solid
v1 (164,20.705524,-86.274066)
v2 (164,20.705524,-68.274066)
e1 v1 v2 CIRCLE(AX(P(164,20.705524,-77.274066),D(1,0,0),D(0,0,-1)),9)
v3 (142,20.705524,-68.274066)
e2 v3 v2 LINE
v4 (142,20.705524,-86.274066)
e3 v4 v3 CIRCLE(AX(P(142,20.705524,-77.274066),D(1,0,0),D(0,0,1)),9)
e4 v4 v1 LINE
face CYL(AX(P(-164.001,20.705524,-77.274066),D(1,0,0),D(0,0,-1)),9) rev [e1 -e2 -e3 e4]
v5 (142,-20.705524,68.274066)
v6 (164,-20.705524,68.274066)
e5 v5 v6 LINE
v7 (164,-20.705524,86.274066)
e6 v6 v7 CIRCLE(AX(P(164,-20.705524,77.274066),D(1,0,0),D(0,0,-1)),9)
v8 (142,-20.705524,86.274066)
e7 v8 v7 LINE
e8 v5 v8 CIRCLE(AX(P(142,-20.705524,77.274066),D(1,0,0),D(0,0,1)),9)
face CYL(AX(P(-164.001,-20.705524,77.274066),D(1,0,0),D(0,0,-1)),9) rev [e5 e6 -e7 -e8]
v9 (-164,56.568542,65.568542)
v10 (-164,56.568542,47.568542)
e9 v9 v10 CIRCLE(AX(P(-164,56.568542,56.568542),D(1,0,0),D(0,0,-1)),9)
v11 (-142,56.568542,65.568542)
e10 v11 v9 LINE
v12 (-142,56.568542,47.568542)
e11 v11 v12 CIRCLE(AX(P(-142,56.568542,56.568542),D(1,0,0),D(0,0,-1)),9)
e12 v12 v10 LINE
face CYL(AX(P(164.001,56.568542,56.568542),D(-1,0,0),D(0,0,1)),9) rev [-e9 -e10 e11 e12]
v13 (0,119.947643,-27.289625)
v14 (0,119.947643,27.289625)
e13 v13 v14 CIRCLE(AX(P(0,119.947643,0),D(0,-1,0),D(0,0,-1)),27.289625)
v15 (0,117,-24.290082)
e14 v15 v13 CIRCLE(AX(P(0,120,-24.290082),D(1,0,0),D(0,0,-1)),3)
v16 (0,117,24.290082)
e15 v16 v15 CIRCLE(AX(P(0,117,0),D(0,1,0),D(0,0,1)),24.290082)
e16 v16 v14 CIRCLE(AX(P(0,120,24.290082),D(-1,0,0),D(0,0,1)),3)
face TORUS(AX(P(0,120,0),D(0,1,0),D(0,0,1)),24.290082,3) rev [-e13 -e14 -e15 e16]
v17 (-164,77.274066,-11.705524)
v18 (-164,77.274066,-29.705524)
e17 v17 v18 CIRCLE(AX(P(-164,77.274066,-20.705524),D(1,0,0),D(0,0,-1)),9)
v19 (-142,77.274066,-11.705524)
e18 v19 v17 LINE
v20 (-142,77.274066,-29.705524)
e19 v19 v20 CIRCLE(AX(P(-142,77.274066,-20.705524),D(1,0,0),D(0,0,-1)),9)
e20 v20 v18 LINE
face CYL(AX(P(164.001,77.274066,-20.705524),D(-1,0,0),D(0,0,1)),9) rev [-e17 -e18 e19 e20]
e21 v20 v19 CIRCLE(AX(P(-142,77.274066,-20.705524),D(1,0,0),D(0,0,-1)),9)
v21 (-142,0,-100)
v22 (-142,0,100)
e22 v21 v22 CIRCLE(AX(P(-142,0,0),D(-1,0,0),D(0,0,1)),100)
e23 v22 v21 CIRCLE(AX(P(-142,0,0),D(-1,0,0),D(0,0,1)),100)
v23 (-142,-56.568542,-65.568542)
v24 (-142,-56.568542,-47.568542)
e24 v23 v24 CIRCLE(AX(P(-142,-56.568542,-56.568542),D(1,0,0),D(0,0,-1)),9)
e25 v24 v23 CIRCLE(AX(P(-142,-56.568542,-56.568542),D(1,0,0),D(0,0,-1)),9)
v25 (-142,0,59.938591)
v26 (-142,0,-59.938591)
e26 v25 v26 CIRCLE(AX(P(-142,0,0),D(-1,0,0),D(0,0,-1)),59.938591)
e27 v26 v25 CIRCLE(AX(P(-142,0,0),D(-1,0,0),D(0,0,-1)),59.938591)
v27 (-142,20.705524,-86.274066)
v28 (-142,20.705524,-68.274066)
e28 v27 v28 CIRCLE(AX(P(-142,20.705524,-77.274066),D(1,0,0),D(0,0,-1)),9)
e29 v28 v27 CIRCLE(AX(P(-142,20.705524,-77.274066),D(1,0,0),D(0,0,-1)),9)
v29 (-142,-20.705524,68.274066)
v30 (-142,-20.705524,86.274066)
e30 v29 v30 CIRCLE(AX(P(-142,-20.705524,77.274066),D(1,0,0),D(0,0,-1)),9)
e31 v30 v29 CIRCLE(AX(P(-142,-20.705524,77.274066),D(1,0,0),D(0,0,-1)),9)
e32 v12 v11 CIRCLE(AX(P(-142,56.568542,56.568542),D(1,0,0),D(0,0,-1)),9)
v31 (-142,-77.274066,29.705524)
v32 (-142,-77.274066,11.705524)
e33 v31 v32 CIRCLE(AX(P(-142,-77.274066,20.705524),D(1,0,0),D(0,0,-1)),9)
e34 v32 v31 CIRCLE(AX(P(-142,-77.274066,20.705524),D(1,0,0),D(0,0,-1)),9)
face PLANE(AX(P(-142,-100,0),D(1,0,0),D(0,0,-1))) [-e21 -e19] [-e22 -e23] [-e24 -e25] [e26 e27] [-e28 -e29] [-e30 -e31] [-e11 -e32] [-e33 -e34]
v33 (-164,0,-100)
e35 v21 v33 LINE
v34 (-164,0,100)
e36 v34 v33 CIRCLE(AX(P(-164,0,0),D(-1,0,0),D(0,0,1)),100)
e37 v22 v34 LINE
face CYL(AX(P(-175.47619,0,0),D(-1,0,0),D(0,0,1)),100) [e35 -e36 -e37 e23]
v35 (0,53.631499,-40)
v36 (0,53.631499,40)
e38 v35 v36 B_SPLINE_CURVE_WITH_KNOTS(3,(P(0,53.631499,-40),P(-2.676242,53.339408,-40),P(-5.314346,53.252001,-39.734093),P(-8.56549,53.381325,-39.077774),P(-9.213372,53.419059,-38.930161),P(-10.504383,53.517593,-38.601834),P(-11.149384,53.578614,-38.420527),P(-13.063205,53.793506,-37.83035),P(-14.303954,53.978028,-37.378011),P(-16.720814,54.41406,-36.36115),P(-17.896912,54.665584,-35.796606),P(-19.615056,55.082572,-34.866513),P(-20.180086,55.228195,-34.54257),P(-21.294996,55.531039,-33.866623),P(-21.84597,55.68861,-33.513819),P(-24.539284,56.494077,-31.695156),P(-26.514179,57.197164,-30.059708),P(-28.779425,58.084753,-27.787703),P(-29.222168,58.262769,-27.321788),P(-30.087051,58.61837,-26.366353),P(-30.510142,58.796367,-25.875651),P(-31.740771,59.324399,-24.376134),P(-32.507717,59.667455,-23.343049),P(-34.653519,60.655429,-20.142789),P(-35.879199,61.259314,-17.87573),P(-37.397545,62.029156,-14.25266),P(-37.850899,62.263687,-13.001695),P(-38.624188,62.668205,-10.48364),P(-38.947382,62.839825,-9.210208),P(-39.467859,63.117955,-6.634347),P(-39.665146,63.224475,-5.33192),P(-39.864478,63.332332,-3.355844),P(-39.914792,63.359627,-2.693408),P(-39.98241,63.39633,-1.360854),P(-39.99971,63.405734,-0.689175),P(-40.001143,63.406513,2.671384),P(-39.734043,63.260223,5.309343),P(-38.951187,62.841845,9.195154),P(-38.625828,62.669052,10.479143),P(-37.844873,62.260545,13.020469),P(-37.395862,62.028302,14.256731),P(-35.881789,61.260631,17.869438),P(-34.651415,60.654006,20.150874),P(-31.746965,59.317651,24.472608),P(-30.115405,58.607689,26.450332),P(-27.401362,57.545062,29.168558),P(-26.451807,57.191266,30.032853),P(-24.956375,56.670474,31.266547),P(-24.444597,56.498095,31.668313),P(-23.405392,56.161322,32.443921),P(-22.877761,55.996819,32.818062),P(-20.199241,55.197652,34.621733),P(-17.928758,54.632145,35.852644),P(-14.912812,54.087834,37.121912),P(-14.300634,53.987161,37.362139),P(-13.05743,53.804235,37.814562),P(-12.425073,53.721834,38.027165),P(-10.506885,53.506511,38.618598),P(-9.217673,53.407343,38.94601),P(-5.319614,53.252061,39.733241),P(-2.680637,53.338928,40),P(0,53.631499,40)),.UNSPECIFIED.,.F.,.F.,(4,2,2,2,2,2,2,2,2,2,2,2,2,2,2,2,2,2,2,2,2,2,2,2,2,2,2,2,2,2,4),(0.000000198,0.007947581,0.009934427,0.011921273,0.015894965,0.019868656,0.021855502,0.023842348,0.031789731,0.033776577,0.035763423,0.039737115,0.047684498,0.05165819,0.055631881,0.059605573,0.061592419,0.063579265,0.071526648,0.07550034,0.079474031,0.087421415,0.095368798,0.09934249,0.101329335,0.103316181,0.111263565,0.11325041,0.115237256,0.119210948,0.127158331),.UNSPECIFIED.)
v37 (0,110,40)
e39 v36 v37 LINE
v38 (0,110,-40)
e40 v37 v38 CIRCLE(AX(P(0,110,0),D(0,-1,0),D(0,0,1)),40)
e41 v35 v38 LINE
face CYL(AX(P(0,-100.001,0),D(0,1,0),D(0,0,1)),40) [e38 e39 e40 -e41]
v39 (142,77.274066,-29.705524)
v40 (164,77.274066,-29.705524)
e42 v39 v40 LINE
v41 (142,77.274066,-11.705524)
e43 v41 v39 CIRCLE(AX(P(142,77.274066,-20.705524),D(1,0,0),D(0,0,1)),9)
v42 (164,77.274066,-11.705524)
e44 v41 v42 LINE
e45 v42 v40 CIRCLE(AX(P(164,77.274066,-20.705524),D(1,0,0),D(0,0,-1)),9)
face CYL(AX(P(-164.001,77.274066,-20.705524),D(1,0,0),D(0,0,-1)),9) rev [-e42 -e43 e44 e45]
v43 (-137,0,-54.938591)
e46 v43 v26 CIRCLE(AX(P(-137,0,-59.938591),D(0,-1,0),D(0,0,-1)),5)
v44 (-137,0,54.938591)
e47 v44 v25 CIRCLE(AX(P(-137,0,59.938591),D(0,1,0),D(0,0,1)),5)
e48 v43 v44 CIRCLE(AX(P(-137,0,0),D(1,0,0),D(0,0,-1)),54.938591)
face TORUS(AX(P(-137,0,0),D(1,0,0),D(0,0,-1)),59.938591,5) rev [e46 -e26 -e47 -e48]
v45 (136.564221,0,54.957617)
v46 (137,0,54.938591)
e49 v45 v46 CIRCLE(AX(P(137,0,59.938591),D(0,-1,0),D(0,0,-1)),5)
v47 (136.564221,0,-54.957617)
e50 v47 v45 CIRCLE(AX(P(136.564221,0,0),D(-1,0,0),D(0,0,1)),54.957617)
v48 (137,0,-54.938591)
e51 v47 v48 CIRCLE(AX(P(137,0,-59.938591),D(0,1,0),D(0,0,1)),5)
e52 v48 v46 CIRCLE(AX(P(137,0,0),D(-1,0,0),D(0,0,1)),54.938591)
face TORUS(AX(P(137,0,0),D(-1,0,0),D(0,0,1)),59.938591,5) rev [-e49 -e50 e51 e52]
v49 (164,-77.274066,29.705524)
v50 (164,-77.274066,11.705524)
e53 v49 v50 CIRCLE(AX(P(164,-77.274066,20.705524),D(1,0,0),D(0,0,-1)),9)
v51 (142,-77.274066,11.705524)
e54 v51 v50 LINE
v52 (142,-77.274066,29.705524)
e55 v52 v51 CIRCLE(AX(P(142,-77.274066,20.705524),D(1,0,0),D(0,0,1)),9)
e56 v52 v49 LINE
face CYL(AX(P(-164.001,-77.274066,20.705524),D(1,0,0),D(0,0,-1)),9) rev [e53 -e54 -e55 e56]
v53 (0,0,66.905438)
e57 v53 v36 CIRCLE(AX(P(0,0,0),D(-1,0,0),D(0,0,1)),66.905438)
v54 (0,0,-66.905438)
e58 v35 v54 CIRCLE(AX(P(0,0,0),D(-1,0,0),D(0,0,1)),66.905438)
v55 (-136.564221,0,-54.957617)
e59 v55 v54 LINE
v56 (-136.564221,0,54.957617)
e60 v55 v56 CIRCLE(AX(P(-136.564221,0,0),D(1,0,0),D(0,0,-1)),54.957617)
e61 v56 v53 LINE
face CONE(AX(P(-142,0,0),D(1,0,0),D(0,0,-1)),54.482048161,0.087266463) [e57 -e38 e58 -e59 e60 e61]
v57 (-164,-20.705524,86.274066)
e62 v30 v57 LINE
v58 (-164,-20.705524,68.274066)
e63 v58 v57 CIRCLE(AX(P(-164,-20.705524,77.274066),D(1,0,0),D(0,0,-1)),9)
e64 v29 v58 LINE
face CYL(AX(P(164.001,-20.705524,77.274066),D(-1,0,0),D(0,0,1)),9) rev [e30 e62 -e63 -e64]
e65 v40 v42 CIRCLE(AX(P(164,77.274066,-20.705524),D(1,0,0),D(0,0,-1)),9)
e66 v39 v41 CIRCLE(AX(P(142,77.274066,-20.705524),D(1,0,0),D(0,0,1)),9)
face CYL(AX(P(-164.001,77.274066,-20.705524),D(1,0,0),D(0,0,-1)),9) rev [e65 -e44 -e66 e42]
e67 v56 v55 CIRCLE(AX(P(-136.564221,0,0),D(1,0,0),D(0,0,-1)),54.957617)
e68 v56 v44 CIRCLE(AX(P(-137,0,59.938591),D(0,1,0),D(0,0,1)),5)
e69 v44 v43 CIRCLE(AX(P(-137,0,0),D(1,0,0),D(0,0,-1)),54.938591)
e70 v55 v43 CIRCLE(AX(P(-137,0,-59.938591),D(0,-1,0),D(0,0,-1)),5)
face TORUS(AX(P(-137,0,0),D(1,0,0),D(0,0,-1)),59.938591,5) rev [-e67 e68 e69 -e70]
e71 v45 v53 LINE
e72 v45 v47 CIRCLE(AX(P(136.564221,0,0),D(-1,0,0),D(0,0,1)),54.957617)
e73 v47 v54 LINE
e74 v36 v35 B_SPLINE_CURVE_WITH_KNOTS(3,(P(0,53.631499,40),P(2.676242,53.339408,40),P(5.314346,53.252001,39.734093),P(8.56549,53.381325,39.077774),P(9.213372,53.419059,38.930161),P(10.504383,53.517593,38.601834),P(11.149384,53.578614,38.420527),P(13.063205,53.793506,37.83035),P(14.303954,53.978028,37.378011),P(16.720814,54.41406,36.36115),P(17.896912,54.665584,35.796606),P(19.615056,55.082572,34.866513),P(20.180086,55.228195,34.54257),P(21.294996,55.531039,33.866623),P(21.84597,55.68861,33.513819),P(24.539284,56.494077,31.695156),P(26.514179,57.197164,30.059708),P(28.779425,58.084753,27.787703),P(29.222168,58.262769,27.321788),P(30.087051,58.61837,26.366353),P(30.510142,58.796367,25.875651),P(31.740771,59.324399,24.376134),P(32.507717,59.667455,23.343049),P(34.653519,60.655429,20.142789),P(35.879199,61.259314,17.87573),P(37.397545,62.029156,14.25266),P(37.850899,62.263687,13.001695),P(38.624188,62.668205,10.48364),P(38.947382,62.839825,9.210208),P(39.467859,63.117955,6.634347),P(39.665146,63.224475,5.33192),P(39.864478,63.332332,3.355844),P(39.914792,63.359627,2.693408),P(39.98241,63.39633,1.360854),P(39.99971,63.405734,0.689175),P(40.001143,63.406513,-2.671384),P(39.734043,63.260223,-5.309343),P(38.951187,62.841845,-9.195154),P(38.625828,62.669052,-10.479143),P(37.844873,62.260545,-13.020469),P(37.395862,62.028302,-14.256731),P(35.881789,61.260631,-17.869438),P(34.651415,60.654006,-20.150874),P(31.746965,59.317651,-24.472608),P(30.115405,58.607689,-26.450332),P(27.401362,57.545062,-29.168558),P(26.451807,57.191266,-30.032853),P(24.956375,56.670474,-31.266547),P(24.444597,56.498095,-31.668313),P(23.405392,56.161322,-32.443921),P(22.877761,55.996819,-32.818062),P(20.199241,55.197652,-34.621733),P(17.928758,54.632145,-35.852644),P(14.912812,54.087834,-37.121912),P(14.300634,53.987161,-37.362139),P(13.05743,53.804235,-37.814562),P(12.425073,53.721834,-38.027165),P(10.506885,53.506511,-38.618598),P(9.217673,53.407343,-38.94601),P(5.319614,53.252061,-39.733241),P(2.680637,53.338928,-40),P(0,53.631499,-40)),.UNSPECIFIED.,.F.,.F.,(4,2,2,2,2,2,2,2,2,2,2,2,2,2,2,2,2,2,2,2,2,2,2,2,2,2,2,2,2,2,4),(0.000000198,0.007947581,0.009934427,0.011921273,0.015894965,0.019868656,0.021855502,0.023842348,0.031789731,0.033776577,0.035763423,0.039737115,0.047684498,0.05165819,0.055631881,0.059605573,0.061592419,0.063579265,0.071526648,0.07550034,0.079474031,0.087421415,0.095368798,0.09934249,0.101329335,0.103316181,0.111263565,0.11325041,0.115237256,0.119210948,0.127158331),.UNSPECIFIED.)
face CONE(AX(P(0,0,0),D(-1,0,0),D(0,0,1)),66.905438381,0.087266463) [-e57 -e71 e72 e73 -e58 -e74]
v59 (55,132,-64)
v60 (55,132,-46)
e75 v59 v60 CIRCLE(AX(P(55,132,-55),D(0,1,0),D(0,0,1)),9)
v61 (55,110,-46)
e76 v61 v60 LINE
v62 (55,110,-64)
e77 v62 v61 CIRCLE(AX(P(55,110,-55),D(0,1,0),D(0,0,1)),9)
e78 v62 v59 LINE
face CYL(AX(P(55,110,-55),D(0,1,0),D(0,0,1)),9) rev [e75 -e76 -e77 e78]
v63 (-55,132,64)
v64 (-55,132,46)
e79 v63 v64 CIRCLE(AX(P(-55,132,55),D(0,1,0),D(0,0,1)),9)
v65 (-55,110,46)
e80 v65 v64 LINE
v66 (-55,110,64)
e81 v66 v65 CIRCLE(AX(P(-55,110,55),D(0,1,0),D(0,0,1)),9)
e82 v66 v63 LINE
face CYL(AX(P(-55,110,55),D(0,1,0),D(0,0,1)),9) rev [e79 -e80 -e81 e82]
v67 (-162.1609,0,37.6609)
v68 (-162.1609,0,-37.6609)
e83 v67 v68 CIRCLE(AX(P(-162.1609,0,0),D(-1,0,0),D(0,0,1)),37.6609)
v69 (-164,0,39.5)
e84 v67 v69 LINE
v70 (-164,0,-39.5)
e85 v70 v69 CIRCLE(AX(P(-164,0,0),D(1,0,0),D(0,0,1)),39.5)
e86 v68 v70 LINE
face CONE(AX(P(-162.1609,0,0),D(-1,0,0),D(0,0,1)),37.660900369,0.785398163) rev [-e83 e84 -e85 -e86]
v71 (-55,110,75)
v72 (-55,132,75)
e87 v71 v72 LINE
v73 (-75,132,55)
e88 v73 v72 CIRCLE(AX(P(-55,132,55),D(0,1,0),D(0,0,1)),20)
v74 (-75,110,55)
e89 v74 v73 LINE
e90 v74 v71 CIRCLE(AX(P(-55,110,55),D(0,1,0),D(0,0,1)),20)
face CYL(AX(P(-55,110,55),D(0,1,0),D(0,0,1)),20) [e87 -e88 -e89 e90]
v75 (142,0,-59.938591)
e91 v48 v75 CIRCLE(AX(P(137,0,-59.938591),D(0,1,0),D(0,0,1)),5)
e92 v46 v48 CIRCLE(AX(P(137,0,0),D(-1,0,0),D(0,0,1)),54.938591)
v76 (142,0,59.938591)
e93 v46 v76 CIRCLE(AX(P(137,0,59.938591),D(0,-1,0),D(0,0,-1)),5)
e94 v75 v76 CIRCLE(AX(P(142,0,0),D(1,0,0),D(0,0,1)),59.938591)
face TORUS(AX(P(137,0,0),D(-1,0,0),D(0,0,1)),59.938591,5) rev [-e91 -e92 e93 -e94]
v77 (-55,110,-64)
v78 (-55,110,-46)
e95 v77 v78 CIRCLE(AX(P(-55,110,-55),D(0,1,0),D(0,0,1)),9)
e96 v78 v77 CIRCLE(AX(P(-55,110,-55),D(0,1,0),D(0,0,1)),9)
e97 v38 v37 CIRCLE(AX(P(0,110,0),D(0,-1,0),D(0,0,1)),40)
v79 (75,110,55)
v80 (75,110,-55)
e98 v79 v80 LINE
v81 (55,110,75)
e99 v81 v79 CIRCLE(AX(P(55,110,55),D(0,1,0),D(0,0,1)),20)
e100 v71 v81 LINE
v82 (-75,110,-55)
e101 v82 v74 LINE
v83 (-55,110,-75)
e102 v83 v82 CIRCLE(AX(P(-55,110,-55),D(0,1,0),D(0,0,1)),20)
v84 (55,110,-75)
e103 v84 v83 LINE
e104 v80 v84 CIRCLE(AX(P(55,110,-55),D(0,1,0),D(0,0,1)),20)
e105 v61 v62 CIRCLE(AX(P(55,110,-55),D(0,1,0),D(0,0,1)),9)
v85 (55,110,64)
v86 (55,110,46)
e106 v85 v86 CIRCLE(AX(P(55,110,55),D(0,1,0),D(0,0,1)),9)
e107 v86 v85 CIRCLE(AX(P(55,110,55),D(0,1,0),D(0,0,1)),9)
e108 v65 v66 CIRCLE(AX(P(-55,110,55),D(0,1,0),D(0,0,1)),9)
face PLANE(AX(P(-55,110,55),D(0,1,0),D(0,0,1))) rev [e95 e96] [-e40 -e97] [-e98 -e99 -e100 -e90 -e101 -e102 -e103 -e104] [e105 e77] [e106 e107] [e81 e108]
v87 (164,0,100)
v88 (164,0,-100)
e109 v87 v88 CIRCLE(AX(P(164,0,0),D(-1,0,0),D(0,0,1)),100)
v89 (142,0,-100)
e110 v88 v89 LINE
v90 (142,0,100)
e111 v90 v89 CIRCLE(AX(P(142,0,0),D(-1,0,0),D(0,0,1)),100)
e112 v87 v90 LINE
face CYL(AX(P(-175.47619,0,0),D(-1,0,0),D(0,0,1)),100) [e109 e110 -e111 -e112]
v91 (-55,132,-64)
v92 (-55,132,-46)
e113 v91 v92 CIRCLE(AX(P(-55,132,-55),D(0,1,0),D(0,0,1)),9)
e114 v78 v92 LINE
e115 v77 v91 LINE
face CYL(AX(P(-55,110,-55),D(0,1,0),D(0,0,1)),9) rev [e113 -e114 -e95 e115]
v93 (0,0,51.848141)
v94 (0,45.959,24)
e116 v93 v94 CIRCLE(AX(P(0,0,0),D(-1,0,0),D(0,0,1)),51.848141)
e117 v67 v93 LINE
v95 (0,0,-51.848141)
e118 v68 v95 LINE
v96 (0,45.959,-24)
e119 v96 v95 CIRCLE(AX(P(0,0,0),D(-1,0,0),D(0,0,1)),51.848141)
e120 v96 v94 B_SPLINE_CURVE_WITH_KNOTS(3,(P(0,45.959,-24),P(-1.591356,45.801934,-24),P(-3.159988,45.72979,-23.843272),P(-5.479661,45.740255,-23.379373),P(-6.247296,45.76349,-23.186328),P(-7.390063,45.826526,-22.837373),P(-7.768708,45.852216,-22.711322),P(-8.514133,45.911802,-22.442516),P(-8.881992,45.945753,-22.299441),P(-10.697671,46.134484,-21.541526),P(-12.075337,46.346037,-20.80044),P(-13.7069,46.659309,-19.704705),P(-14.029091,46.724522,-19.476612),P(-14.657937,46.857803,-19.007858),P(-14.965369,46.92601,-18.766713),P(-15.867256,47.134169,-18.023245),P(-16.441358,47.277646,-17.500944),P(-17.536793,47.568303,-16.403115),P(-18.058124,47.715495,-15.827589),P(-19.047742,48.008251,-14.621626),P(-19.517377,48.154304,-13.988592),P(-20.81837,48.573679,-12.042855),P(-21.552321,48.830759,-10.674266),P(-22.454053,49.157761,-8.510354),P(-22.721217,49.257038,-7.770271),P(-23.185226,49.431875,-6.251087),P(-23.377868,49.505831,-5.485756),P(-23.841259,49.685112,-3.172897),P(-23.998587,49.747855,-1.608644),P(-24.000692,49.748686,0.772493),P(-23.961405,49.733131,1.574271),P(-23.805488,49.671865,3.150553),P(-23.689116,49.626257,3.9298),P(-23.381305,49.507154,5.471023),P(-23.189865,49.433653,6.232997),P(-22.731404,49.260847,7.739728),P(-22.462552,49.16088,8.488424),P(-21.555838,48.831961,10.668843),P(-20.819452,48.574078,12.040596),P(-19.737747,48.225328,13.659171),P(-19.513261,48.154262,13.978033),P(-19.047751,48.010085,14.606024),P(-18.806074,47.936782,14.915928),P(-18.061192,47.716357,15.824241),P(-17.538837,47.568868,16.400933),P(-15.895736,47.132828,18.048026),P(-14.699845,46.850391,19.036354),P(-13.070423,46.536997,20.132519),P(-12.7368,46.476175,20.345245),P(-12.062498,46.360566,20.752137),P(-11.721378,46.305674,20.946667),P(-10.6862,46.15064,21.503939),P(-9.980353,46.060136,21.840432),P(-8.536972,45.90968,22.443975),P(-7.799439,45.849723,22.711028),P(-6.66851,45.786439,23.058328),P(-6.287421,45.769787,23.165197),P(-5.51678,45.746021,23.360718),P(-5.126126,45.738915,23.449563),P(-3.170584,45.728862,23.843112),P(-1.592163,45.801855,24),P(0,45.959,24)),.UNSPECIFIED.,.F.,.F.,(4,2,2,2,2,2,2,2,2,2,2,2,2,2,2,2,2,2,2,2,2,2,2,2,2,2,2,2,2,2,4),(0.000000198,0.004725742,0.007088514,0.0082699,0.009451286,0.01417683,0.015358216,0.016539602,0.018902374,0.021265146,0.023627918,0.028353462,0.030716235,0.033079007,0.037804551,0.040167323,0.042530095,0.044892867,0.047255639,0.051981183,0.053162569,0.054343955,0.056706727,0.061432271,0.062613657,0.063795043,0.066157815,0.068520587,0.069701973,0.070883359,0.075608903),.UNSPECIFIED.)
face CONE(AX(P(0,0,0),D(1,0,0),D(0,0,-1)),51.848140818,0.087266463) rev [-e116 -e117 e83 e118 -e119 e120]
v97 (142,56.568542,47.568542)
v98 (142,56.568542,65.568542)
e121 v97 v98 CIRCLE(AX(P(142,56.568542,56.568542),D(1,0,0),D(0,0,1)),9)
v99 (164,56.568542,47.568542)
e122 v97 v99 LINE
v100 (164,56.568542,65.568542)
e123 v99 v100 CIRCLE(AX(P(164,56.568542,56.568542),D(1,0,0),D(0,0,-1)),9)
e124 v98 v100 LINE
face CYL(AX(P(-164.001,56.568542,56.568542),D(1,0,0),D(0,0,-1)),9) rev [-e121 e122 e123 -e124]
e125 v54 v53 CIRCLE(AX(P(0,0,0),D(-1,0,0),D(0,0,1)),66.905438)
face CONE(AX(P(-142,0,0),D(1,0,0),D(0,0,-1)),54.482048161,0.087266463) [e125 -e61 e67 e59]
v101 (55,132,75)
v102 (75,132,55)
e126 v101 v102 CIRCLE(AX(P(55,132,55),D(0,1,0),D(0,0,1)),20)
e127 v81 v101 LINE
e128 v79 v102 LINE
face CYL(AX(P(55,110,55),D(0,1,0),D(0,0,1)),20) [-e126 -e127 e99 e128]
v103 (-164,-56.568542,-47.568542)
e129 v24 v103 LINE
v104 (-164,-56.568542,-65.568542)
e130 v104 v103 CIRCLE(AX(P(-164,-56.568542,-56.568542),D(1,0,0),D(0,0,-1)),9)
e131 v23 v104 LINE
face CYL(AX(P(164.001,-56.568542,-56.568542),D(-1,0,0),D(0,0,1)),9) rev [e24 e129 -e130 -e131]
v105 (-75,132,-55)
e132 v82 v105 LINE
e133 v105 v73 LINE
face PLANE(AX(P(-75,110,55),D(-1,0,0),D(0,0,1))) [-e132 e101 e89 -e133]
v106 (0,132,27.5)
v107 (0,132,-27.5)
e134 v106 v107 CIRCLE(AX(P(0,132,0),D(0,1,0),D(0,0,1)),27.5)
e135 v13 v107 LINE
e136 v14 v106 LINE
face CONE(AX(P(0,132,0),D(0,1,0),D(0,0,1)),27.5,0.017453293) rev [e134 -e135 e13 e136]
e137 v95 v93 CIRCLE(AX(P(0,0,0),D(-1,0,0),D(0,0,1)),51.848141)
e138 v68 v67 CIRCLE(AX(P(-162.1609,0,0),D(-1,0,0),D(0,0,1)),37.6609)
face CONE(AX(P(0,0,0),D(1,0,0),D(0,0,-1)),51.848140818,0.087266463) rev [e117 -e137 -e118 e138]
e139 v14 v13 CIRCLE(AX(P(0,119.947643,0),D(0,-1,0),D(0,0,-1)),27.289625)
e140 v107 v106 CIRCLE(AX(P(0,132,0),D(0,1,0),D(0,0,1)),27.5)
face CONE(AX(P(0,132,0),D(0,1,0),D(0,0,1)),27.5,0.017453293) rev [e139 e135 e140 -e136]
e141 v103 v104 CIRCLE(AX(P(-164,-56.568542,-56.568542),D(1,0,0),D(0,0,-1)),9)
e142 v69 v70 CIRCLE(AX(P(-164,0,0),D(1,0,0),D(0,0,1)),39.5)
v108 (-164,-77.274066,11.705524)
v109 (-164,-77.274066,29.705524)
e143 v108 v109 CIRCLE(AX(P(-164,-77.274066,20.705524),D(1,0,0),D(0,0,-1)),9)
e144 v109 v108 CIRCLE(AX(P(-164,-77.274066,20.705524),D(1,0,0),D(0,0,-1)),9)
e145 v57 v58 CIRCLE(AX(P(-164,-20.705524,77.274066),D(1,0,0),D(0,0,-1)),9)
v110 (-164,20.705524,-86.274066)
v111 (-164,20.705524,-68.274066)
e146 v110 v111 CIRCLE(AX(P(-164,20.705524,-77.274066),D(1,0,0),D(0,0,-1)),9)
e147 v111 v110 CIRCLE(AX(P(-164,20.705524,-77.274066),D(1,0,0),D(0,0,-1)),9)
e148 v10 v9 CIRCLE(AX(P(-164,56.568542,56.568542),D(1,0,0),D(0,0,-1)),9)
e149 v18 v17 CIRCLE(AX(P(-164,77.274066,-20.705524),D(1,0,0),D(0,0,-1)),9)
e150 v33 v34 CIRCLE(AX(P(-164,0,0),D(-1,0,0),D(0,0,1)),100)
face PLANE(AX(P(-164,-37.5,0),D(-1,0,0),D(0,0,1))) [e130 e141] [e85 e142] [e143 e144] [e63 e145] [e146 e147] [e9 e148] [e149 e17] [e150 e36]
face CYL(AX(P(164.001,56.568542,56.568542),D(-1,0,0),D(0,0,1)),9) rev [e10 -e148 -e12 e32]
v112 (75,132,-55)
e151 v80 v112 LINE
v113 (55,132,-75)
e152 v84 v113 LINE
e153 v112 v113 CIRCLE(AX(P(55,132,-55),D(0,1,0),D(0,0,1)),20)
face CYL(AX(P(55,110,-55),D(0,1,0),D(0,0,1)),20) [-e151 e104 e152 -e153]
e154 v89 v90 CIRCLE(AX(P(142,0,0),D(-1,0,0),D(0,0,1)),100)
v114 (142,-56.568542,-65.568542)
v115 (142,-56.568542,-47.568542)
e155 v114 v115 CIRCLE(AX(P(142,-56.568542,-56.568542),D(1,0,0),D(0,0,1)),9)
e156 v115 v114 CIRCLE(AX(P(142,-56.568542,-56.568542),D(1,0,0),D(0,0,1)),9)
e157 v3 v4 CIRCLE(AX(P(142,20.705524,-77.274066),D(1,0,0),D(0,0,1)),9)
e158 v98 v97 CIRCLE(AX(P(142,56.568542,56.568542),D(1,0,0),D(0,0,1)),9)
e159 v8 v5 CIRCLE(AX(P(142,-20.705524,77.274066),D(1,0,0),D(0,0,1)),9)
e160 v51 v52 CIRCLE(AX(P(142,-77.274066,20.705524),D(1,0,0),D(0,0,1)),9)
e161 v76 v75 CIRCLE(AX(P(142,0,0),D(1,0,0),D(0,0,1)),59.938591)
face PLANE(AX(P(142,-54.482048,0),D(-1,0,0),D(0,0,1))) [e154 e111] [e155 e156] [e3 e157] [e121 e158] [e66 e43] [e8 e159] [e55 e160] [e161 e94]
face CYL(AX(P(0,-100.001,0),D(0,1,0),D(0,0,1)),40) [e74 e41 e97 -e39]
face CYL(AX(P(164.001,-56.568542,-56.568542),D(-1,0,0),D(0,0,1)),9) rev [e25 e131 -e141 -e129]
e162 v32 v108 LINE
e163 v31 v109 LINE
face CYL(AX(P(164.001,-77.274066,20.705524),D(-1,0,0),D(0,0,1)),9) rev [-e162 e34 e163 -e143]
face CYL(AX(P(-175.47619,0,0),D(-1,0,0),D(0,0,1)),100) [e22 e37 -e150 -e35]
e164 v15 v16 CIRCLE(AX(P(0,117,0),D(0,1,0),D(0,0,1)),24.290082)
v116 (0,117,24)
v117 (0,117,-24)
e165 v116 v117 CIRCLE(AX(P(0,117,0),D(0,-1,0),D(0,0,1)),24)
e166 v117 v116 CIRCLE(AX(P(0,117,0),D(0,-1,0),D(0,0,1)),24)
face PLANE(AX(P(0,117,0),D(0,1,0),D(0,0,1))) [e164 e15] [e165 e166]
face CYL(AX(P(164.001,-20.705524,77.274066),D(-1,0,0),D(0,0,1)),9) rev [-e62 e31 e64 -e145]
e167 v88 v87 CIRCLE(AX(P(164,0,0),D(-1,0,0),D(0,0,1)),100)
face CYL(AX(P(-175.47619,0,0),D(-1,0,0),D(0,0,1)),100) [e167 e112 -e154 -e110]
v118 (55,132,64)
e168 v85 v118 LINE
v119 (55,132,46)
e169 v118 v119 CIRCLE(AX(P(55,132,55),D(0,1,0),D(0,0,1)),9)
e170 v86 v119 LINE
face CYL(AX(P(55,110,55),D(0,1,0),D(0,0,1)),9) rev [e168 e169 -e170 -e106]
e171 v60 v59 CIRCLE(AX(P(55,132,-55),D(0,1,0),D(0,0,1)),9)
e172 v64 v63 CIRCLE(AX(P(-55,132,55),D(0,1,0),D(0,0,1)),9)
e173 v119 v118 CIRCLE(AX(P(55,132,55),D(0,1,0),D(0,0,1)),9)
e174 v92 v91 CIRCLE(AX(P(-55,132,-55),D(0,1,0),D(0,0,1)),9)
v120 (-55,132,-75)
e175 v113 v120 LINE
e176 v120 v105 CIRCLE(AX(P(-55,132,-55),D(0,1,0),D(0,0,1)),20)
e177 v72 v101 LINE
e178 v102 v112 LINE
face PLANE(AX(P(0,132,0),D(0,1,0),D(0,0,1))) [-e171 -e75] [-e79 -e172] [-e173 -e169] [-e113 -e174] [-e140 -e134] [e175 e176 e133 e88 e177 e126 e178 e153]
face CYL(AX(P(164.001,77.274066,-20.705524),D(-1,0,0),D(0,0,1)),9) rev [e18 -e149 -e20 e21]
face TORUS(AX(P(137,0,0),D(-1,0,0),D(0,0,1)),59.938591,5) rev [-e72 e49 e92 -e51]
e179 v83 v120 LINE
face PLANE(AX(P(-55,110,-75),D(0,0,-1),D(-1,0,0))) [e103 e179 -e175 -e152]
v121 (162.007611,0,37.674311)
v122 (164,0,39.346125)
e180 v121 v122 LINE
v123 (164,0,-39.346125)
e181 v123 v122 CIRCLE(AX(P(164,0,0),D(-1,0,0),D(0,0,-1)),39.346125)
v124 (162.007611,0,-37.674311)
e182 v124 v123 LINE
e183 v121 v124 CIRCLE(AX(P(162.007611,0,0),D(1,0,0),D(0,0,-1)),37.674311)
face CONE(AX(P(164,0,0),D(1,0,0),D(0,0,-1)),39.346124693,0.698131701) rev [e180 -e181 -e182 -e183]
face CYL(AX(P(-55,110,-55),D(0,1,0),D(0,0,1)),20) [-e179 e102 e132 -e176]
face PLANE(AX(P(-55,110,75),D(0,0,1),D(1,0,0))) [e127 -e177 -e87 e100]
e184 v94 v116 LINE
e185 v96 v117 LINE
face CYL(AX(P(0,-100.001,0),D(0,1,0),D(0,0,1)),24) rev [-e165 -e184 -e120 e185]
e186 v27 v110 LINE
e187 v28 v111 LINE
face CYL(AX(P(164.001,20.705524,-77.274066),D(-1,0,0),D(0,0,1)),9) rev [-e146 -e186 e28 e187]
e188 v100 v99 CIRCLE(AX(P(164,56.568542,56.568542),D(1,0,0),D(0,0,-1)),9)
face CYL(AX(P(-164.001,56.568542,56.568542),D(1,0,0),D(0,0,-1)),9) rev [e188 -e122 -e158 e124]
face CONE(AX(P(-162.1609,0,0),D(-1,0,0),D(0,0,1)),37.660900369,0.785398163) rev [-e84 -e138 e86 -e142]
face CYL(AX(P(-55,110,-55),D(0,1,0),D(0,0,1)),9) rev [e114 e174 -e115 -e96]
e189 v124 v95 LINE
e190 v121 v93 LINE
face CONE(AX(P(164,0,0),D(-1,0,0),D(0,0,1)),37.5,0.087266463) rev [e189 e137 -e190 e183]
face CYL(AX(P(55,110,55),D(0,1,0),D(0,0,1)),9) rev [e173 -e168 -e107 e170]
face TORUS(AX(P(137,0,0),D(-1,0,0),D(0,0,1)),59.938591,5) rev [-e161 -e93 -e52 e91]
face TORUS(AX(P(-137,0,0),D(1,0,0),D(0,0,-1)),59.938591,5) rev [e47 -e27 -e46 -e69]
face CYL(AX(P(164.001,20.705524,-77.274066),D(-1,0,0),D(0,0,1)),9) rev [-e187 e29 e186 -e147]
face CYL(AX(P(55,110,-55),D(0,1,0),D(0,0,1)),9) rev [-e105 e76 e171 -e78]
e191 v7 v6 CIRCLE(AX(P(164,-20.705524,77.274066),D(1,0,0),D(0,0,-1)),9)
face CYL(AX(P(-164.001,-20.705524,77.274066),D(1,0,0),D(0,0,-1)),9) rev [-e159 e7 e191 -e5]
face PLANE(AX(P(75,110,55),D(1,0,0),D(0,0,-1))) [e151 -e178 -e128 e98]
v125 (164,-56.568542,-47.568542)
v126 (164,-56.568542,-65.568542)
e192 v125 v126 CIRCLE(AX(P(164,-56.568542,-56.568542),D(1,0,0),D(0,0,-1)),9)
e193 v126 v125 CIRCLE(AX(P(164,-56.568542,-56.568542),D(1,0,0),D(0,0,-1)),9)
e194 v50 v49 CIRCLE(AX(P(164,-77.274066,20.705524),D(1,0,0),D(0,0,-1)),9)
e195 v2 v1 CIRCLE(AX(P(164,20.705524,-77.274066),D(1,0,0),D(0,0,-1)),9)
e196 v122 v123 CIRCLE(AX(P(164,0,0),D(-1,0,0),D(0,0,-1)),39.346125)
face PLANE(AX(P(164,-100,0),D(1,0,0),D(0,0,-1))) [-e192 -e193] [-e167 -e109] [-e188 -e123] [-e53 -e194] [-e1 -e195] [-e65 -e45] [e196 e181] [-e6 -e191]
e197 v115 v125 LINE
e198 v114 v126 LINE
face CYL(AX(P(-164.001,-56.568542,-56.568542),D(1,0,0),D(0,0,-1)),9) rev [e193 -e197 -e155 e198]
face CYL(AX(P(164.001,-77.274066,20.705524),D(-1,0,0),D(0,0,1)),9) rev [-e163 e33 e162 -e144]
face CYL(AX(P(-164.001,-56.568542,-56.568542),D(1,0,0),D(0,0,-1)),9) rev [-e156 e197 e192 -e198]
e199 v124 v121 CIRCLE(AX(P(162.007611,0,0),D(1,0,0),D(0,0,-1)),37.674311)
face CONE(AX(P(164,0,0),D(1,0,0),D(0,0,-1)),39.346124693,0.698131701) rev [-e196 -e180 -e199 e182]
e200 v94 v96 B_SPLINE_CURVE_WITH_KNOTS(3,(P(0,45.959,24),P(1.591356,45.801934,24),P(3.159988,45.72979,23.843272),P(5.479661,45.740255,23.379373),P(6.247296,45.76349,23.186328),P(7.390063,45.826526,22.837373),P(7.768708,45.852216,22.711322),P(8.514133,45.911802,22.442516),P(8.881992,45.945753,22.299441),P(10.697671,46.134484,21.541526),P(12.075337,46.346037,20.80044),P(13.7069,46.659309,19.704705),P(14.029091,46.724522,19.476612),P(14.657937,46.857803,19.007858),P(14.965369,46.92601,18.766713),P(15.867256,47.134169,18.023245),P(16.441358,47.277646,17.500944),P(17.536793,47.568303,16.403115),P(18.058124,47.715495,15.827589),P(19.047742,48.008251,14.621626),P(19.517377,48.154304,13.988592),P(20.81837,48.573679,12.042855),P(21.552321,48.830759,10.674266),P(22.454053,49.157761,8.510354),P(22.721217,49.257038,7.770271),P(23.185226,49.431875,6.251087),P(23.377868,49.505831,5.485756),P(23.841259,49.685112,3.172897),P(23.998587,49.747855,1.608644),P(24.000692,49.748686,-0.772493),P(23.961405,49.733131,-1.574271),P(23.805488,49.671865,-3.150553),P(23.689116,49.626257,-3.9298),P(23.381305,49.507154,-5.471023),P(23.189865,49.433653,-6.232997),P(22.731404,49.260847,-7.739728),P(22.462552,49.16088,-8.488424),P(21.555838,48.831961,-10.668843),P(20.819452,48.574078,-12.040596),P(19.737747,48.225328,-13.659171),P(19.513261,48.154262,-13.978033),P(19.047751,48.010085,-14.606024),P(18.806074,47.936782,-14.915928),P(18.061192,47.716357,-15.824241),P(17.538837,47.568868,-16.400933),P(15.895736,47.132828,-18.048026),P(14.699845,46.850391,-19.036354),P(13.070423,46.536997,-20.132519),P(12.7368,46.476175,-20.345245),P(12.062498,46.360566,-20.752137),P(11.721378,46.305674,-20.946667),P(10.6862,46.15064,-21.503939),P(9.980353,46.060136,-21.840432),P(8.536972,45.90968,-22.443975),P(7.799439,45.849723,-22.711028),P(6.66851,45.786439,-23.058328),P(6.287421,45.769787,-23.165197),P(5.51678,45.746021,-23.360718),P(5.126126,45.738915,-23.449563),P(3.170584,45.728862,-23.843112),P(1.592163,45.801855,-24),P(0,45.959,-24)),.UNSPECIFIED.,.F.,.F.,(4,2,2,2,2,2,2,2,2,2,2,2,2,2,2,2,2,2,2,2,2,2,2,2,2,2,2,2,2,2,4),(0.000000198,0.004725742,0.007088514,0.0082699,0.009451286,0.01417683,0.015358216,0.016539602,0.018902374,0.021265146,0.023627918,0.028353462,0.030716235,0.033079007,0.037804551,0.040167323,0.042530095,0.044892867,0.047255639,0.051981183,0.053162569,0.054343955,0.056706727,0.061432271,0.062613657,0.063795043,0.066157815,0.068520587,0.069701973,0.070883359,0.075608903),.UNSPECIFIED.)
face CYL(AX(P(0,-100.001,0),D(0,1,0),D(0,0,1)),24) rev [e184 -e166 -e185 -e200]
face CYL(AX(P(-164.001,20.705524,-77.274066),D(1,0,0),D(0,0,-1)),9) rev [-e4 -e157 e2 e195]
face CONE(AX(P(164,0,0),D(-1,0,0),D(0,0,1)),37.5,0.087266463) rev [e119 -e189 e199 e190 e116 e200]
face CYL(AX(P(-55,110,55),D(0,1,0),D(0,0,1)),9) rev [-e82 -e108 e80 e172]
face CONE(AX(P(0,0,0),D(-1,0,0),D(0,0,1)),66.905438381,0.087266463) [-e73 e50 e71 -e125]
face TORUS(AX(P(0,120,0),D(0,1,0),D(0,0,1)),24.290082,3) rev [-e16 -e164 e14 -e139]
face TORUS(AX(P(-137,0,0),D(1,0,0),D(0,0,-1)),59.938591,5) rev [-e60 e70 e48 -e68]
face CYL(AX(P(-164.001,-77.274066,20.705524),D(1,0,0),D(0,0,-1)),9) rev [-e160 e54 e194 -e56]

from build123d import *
from OCP.BRepFilletAPI import BRepFilletAPI_MakeChamfer

# Parameters (mm, degrees)
BODY_EDGE_CHAMFER_2MM_SIZE        = 2
BODY_EDGE_CHAMFER_2MM_SIZE2       = 1.846124693
BONNET_NECK_80_REACH              = 303.198
BONNET_NECK_SKETCH_R              = 40
TOP_FLANGE_SKETCH_R               = 9
TOP_FLANGE_150X150_DEPTH          = 22
STEM_BORE_48_REACH                = 303.198
STEM_BORE_SKETCH_R                = 24
STEM_COUNTERBORE_SKETCH_R         = 27.5
STEM_COUNTERBORE_55_DEPTH         = 15
STEM_COUNTERBORE_55_DRAFT         = -1
BODY_FILLET_R5_R                  = 5
END_FLANGE_BOLT_HOLES_6X_18_REACH = 369.434
END_FLANGE_BOLT_HOLES_SKETCH_R    = 9
COUNTERBORE_FILLET_R3_R           = 3


with BuildPart() as part:
    # Body Profile Sketch → Valve Body Revolve (revolve)
    with BuildSketch(Plane.XY, mode=Mode.PRIVATE) as valve_body_revolve_sk:
        Polygon((-142, -54.482048161), (0, -66.905438381), (142, -54.482048161), (142, -100), (164, -100), (164, -37.5), (0, -51.848140818), (-164, -37.5), (-164, -100), (-142, -100), align=None)
    revolve(valve_body_revolve_sk.sketch.rotate(Axis((-175.476190476, 0, 0), (1, 0, 0)), 270), axis=Axis((-175.476190476, 0, 0), (1, 0, 0)))

    # Body Edge Chamfer 2mm: one chamfer whose edges measure the first distance from different faces: ONE call of the kernel's chamfer builder (chamfer() names one face for all edges)
    body_edge_chamfer_2mm_edges_1 = [part.edges().sort_by_distance(p)[0] for p in [
        (164, 0, -37.5),
    ]]
    body_edge_chamfer_2mm_side_1 = [part.faces().sort_by_distance(p)[0] for p in [
        (82, 0, -44.674070409),
    ]]
    body_edge_chamfer_2mm_edges_2 = [part.edges().sort_by_distance(p)[0] for p in [
        (-164, 0, -37.5),
    ]]
    body_edge_chamfer_2mm_side_2 = [part.faces().sort_by_distance(p)[0] for p in [
        (-164, 0, -40.328427125),
    ]]
    body_edge_chamfer_2mm = BRepFilletAPI_MakeChamfer(part.part.solid().wrapped)
    for e in body_edge_chamfer_2mm_edges_1:
        body_edge_chamfer_2mm.Add(BODY_EDGE_CHAMFER_2MM_SIZE, BODY_EDGE_CHAMFER_2MM_SIZE2, e.wrapped, body_edge_chamfer_2mm_side_1[0].wrapped)  # the first distance lies on this face
    for e in body_edge_chamfer_2mm_edges_2:
        body_edge_chamfer_2mm.Add(BODY_EDGE_CHAMFER_2MM_SIZE, BODY_EDGE_CHAMFER_2MM_SIZE2, e.wrapped, body_edge_chamfer_2mm_side_2[0].wrapped)  # the first distance lies on this face
    add(Compound.cast(body_edge_chamfer_2mm.Shape()), mode=Mode.REPLACE)

    # Bonnet Neck Sketch → Bonnet Neck Ø80 (add, up to next)
    with BuildSketch(Plane(origin=(0, 132, 0), x_dir=(1, 0, 0), z_dir=(0, 1, 0)), mode=Mode.PRIVATE) as bonnet_neck_80_sk1:
        with Locations(Location((0, 0, 0), (0, 0, 270))):
            Circle(BONNET_NECK_SKETCH_R)
    bonnet_neck_80_tool1 = extrude(bonnet_neck_80_sk1.sketch, amount=-BONNET_NECK_80_REACH, mode=Mode.PRIVATE) - part.part
    add(bonnet_neck_80_tool1.solids().sort_by_distance((0, 132, 0))[0])

    # Top Flange Sketch → Top Flange 150x150 (add)
    with BuildSketch(Plane(origin=(0, 132, 0), x_dir=(1, 0, 0), z_dir=(0, 1, 0))):
        with BuildLine():
            Line((-55, -75), (55, -75))
            ThreePointArc((55, -75), (69.142135624, -69.142135624), (75, -55))
            Line((75, -55), (75, 55))
            ThreePointArc((75, 55), (69.142135624, 69.142135624), (55, 75))
            Line((55, 75), (-55, 75))
            ThreePointArc((-55, 75), (-69.142135624, 69.142135624), (-75, 55))
            Line((-75, 55), (-75, -55))
            ThreePointArc((-75, -55), (-69.142135624, -69.142135624), (-55, -75))
        make_face()
        with Locations(Location((-55, 55, 0), (0, 0, 270))):
            Circle(TOP_FLANGE_SKETCH_R, mode=Mode.SUBTRACT)
        with Locations(Location((55, 55, 0), (0, 0, 270))):
            Circle(TOP_FLANGE_SKETCH_R, mode=Mode.SUBTRACT)
        with Locations(Location((55, -55, 0), (0, 0, 270))):
            Circle(TOP_FLANGE_SKETCH_R, mode=Mode.SUBTRACT)
        with Locations(Location((-55, -55, 0), (0, 0, 270))):
            Circle(TOP_FLANGE_SKETCH_R, mode=Mode.SUBTRACT)
    extrude(amount=-TOP_FLANGE_150X150_DEPTH)

    # Stem Bore Sketch → Stem Bore Ø48 (cut, up to next)
    with BuildSketch(Plane(origin=(0, 132, 0), x_dir=(1, 0, 0), z_dir=(0, 1, 0)), mode=Mode.PRIVATE) as stem_bore_48_sk1:
        with Locations(Location((0, 0, 0), (0, 0, 270))):
            Circle(STEM_BORE_SKETCH_R)
    stem_bore_48_tool1 = extrude(stem_bore_48_sk1.sketch, amount=-STEM_BORE_48_REACH, mode=Mode.PRIVATE) & part.part
    add(stem_bore_48_tool1.solids().sort_by_distance((0, 132, 0))[0], mode=Mode.SUBTRACT)


with BuildPart() as stem_counterbore_55_tool:
    # Stem Counterbore Sketch → Stem Counterbore Ø55 (with draft: the straight prism first)
    with BuildSketch(Plane(origin=(0, 132, 0), x_dir=(1, 0, 0), z_dir=(0, 1, 0))):
        Circle(STEM_COUNTERBORE_SKETCH_R)
    extrude(amount=-STEM_COUNTERBORE_55_DEPTH)
    # Stem Counterbore Ø55: the draft: its side faces are tilted about the plane it starts from
    stem_counterbore_55_sides = [stem_counterbore_55_tool.faces().sort_by_distance(p)[0] for p in [
        (-27.5, 124.5, 0),
    ]]
    draft(stem_counterbore_55_sides, Plane(origin=(0, 132, 0), x_dir=(1, 0, 0), z_dir=(0, 1, 0)), STEM_COUNTERBORE_55_DRAFT)


with BuildPart() as part_1:
    add(part.part)

    # Stem Counterbore Ø55: cut by stem_counterbore_55_tool
    add(stem_counterbore_55_tool.part, mode=Mode.SUBTRACT)

    # Body Fillet R5
    body_fillet_r5_edges = [part_1.edges().sort_by_distance(p)[0] for p in [
        (-142, 0, -54.482048161),
        (142, 0, -54.482048161),
    ]]
    fillet(body_fillet_r5_edges, radius=BODY_FILLET_R5_R)

    # End Flange Bolt Holes Sketch → End Flange Bolt Holes 6xØ18 (cut, up to next)
    with BuildSketch(Plane(origin=(164, 0, 0), x_dir=(0, 0, -1), z_dir=(1, 0, 0)), mode=Mode.PRIVATE) as end_flange_bolt_holes_6x_18_sk1:
        with Locations((-77.274066103, -20.705523608)):
            Circle(END_FLANGE_BOLT_HOLES_SKETCH_R)
    end_flange_bolt_holes_6x_18_tool1 = extrude(end_flange_bolt_holes_6x_18_sk1.sketch, amount=-END_FLANGE_BOLT_HOLES_6X_18_REACH, mode=Mode.PRIVATE) & part_1.part
    # End Flange Bolt Holes Sketch → End Flange Bolt Holes 6xØ18 (cut, up to next)
    with BuildSketch(Plane(origin=(164, 0, 0), x_dir=(0, 0, -1), z_dir=(1, 0, 0)), mode=Mode.PRIVATE) as end_flange_bolt_holes_6x_18_sk2:
        with Locations((-56.568542495, 56.568542495)):
            Circle(END_FLANGE_BOLT_HOLES_SKETCH_R)
    end_flange_bolt_holes_6x_18_tool2 = extrude(end_flange_bolt_holes_6x_18_sk2.sketch, amount=-END_FLANGE_BOLT_HOLES_6X_18_REACH, mode=Mode.PRIVATE) & part_1.part
    # End Flange Bolt Holes Sketch → End Flange Bolt Holes 6xØ18 (cut, up to next)
    with BuildSketch(Plane(origin=(164, 0, 0), x_dir=(0, 0, -1), z_dir=(1, 0, 0)), mode=Mode.PRIVATE) as end_flange_bolt_holes_6x_18_sk3:
        with Locations((20.705523608, 77.274066103)):
            Circle(END_FLANGE_BOLT_HOLES_SKETCH_R)
    end_flange_bolt_holes_6x_18_tool3 = extrude(end_flange_bolt_holes_6x_18_sk3.sketch, amount=-END_FLANGE_BOLT_HOLES_6X_18_REACH, mode=Mode.PRIVATE) & part_1.part
    # End Flange Bolt Holes Sketch → End Flange Bolt Holes 6xØ18 (cut, up to next)
    with BuildSketch(Plane(origin=(164, 0, 0), x_dir=(0, 0, -1), z_dir=(1, 0, 0)), mode=Mode.PRIVATE) as end_flange_bolt_holes_6x_18_sk4:
        with Locations((77.274066103, 20.705523608)):
            Circle(END_FLANGE_BOLT_HOLES_SKETCH_R)
    end_flange_bolt_holes_6x_18_tool4 = extrude(end_flange_bolt_holes_6x_18_sk4.sketch, amount=-END_FLANGE_BOLT_HOLES_6X_18_REACH, mode=Mode.PRIVATE) & part_1.part
    # End Flange Bolt Holes Sketch → End Flange Bolt Holes 6xØ18 (cut, up to next)
    with BuildSketch(Plane(origin=(164, 0, 0), x_dir=(0, 0, -1), z_dir=(1, 0, 0)), mode=Mode.PRIVATE) as end_flange_bolt_holes_6x_18_sk5:
        with Locations((56.568542495, -56.568542495)):
            Circle(END_FLANGE_BOLT_HOLES_SKETCH_R)
    end_flange_bolt_holes_6x_18_tool5 = extrude(end_flange_bolt_holes_6x_18_sk5.sketch, amount=-END_FLANGE_BOLT_HOLES_6X_18_REACH, mode=Mode.PRIVATE) & part_1.part
    # End Flange Bolt Holes Sketch → End Flange Bolt Holes 6xØ18 (cut, up to next)
    with BuildSketch(Plane(origin=(164, 0, 0), x_dir=(0, 0, -1), z_dir=(1, 0, 0)), mode=Mode.PRIVATE) as end_flange_bolt_holes_6x_18_sk6:
        with Locations((-20.705523608, -77.274066103)):
            Circle(END_FLANGE_BOLT_HOLES_SKETCH_R)
    end_flange_bolt_holes_6x_18_tool6 = extrude(end_flange_bolt_holes_6x_18_sk6.sketch, amount=-END_FLANGE_BOLT_HOLES_6X_18_REACH, mode=Mode.PRIVATE) & part_1.part
    end_flange_bolt_holes_6x_18_1 = end_flange_bolt_holes_6x_18_tool1.solids().sort_by_distance((164, -20.705524, 77.274066))[0]
    add(end_flange_bolt_holes_6x_18_1, mode=Mode.SUBTRACT)
    end_flange_bolt_holes_6x_18_2 = end_flange_bolt_holes_6x_18_tool2.solids().sort_by_distance((164, 56.568542, 56.568542))[0]
    add(end_flange_bolt_holes_6x_18_2, mode=Mode.SUBTRACT)
    end_flange_bolt_holes_6x_18_3 = end_flange_bolt_holes_6x_18_tool3.solids().sort_by_distance((164, 77.274066, -20.705524))[0]
    add(end_flange_bolt_holes_6x_18_3, mode=Mode.SUBTRACT)
    end_flange_bolt_holes_6x_18_4 = end_flange_bolt_holes_6x_18_tool4.solids().sort_by_distance((164, 20.705524, -77.274066))[0]
    add(end_flange_bolt_holes_6x_18_4, mode=Mode.SUBTRACT)
    end_flange_bolt_holes_6x_18_5 = end_flange_bolt_holes_6x_18_tool5.solids().sort_by_distance((164, -56.568542, -56.568542))[0]
    add(end_flange_bolt_holes_6x_18_5, mode=Mode.SUBTRACT)
    end_flange_bolt_holes_6x_18_6 = end_flange_bolt_holes_6x_18_tool6.solids().sort_by_distance((164, -77.274066, 20.705524))[0]
    add(end_flange_bolt_holes_6x_18_6, mode=Mode.SUBTRACT)
    end_flange_bolt_holes_6x_18 = end_flange_bolt_holes_6x_18_1 + end_flange_bolt_holes_6x_18_2 + end_flange_bolt_holes_6x_18_3 + end_flange_bolt_holes_6x_18_4 + end_flange_bolt_holes_6x_18_5 + end_flange_bolt_holes_6x_18_6  # End Flange Bolt Holes 6xØ18 as one shape, for the pattern or mirror that repeats it

    # Counterbore Fillet R3
    counterbore_fillet_r3_edges = [part_1.edges().sort_by_distance(p)[0] for p in [
        (-27.238174026, 117, 0),
    ]]
    fillet(counterbore_fillet_r3_edges, radius=COUNTERBORE_FILLET_R3_R)

    # End Flange Bolt Holes Mirror: End Flange Bolt Holes 6xØ18 across plane
    add(end_flange_bolt_holes_6x_18.mirror(Plane(origin=(0, 0, 0), x_dir=(0, 0, 1), z_dir=(1, 0, 0))), mode=Mode.SUBTRACT)


solid = part_1.part
